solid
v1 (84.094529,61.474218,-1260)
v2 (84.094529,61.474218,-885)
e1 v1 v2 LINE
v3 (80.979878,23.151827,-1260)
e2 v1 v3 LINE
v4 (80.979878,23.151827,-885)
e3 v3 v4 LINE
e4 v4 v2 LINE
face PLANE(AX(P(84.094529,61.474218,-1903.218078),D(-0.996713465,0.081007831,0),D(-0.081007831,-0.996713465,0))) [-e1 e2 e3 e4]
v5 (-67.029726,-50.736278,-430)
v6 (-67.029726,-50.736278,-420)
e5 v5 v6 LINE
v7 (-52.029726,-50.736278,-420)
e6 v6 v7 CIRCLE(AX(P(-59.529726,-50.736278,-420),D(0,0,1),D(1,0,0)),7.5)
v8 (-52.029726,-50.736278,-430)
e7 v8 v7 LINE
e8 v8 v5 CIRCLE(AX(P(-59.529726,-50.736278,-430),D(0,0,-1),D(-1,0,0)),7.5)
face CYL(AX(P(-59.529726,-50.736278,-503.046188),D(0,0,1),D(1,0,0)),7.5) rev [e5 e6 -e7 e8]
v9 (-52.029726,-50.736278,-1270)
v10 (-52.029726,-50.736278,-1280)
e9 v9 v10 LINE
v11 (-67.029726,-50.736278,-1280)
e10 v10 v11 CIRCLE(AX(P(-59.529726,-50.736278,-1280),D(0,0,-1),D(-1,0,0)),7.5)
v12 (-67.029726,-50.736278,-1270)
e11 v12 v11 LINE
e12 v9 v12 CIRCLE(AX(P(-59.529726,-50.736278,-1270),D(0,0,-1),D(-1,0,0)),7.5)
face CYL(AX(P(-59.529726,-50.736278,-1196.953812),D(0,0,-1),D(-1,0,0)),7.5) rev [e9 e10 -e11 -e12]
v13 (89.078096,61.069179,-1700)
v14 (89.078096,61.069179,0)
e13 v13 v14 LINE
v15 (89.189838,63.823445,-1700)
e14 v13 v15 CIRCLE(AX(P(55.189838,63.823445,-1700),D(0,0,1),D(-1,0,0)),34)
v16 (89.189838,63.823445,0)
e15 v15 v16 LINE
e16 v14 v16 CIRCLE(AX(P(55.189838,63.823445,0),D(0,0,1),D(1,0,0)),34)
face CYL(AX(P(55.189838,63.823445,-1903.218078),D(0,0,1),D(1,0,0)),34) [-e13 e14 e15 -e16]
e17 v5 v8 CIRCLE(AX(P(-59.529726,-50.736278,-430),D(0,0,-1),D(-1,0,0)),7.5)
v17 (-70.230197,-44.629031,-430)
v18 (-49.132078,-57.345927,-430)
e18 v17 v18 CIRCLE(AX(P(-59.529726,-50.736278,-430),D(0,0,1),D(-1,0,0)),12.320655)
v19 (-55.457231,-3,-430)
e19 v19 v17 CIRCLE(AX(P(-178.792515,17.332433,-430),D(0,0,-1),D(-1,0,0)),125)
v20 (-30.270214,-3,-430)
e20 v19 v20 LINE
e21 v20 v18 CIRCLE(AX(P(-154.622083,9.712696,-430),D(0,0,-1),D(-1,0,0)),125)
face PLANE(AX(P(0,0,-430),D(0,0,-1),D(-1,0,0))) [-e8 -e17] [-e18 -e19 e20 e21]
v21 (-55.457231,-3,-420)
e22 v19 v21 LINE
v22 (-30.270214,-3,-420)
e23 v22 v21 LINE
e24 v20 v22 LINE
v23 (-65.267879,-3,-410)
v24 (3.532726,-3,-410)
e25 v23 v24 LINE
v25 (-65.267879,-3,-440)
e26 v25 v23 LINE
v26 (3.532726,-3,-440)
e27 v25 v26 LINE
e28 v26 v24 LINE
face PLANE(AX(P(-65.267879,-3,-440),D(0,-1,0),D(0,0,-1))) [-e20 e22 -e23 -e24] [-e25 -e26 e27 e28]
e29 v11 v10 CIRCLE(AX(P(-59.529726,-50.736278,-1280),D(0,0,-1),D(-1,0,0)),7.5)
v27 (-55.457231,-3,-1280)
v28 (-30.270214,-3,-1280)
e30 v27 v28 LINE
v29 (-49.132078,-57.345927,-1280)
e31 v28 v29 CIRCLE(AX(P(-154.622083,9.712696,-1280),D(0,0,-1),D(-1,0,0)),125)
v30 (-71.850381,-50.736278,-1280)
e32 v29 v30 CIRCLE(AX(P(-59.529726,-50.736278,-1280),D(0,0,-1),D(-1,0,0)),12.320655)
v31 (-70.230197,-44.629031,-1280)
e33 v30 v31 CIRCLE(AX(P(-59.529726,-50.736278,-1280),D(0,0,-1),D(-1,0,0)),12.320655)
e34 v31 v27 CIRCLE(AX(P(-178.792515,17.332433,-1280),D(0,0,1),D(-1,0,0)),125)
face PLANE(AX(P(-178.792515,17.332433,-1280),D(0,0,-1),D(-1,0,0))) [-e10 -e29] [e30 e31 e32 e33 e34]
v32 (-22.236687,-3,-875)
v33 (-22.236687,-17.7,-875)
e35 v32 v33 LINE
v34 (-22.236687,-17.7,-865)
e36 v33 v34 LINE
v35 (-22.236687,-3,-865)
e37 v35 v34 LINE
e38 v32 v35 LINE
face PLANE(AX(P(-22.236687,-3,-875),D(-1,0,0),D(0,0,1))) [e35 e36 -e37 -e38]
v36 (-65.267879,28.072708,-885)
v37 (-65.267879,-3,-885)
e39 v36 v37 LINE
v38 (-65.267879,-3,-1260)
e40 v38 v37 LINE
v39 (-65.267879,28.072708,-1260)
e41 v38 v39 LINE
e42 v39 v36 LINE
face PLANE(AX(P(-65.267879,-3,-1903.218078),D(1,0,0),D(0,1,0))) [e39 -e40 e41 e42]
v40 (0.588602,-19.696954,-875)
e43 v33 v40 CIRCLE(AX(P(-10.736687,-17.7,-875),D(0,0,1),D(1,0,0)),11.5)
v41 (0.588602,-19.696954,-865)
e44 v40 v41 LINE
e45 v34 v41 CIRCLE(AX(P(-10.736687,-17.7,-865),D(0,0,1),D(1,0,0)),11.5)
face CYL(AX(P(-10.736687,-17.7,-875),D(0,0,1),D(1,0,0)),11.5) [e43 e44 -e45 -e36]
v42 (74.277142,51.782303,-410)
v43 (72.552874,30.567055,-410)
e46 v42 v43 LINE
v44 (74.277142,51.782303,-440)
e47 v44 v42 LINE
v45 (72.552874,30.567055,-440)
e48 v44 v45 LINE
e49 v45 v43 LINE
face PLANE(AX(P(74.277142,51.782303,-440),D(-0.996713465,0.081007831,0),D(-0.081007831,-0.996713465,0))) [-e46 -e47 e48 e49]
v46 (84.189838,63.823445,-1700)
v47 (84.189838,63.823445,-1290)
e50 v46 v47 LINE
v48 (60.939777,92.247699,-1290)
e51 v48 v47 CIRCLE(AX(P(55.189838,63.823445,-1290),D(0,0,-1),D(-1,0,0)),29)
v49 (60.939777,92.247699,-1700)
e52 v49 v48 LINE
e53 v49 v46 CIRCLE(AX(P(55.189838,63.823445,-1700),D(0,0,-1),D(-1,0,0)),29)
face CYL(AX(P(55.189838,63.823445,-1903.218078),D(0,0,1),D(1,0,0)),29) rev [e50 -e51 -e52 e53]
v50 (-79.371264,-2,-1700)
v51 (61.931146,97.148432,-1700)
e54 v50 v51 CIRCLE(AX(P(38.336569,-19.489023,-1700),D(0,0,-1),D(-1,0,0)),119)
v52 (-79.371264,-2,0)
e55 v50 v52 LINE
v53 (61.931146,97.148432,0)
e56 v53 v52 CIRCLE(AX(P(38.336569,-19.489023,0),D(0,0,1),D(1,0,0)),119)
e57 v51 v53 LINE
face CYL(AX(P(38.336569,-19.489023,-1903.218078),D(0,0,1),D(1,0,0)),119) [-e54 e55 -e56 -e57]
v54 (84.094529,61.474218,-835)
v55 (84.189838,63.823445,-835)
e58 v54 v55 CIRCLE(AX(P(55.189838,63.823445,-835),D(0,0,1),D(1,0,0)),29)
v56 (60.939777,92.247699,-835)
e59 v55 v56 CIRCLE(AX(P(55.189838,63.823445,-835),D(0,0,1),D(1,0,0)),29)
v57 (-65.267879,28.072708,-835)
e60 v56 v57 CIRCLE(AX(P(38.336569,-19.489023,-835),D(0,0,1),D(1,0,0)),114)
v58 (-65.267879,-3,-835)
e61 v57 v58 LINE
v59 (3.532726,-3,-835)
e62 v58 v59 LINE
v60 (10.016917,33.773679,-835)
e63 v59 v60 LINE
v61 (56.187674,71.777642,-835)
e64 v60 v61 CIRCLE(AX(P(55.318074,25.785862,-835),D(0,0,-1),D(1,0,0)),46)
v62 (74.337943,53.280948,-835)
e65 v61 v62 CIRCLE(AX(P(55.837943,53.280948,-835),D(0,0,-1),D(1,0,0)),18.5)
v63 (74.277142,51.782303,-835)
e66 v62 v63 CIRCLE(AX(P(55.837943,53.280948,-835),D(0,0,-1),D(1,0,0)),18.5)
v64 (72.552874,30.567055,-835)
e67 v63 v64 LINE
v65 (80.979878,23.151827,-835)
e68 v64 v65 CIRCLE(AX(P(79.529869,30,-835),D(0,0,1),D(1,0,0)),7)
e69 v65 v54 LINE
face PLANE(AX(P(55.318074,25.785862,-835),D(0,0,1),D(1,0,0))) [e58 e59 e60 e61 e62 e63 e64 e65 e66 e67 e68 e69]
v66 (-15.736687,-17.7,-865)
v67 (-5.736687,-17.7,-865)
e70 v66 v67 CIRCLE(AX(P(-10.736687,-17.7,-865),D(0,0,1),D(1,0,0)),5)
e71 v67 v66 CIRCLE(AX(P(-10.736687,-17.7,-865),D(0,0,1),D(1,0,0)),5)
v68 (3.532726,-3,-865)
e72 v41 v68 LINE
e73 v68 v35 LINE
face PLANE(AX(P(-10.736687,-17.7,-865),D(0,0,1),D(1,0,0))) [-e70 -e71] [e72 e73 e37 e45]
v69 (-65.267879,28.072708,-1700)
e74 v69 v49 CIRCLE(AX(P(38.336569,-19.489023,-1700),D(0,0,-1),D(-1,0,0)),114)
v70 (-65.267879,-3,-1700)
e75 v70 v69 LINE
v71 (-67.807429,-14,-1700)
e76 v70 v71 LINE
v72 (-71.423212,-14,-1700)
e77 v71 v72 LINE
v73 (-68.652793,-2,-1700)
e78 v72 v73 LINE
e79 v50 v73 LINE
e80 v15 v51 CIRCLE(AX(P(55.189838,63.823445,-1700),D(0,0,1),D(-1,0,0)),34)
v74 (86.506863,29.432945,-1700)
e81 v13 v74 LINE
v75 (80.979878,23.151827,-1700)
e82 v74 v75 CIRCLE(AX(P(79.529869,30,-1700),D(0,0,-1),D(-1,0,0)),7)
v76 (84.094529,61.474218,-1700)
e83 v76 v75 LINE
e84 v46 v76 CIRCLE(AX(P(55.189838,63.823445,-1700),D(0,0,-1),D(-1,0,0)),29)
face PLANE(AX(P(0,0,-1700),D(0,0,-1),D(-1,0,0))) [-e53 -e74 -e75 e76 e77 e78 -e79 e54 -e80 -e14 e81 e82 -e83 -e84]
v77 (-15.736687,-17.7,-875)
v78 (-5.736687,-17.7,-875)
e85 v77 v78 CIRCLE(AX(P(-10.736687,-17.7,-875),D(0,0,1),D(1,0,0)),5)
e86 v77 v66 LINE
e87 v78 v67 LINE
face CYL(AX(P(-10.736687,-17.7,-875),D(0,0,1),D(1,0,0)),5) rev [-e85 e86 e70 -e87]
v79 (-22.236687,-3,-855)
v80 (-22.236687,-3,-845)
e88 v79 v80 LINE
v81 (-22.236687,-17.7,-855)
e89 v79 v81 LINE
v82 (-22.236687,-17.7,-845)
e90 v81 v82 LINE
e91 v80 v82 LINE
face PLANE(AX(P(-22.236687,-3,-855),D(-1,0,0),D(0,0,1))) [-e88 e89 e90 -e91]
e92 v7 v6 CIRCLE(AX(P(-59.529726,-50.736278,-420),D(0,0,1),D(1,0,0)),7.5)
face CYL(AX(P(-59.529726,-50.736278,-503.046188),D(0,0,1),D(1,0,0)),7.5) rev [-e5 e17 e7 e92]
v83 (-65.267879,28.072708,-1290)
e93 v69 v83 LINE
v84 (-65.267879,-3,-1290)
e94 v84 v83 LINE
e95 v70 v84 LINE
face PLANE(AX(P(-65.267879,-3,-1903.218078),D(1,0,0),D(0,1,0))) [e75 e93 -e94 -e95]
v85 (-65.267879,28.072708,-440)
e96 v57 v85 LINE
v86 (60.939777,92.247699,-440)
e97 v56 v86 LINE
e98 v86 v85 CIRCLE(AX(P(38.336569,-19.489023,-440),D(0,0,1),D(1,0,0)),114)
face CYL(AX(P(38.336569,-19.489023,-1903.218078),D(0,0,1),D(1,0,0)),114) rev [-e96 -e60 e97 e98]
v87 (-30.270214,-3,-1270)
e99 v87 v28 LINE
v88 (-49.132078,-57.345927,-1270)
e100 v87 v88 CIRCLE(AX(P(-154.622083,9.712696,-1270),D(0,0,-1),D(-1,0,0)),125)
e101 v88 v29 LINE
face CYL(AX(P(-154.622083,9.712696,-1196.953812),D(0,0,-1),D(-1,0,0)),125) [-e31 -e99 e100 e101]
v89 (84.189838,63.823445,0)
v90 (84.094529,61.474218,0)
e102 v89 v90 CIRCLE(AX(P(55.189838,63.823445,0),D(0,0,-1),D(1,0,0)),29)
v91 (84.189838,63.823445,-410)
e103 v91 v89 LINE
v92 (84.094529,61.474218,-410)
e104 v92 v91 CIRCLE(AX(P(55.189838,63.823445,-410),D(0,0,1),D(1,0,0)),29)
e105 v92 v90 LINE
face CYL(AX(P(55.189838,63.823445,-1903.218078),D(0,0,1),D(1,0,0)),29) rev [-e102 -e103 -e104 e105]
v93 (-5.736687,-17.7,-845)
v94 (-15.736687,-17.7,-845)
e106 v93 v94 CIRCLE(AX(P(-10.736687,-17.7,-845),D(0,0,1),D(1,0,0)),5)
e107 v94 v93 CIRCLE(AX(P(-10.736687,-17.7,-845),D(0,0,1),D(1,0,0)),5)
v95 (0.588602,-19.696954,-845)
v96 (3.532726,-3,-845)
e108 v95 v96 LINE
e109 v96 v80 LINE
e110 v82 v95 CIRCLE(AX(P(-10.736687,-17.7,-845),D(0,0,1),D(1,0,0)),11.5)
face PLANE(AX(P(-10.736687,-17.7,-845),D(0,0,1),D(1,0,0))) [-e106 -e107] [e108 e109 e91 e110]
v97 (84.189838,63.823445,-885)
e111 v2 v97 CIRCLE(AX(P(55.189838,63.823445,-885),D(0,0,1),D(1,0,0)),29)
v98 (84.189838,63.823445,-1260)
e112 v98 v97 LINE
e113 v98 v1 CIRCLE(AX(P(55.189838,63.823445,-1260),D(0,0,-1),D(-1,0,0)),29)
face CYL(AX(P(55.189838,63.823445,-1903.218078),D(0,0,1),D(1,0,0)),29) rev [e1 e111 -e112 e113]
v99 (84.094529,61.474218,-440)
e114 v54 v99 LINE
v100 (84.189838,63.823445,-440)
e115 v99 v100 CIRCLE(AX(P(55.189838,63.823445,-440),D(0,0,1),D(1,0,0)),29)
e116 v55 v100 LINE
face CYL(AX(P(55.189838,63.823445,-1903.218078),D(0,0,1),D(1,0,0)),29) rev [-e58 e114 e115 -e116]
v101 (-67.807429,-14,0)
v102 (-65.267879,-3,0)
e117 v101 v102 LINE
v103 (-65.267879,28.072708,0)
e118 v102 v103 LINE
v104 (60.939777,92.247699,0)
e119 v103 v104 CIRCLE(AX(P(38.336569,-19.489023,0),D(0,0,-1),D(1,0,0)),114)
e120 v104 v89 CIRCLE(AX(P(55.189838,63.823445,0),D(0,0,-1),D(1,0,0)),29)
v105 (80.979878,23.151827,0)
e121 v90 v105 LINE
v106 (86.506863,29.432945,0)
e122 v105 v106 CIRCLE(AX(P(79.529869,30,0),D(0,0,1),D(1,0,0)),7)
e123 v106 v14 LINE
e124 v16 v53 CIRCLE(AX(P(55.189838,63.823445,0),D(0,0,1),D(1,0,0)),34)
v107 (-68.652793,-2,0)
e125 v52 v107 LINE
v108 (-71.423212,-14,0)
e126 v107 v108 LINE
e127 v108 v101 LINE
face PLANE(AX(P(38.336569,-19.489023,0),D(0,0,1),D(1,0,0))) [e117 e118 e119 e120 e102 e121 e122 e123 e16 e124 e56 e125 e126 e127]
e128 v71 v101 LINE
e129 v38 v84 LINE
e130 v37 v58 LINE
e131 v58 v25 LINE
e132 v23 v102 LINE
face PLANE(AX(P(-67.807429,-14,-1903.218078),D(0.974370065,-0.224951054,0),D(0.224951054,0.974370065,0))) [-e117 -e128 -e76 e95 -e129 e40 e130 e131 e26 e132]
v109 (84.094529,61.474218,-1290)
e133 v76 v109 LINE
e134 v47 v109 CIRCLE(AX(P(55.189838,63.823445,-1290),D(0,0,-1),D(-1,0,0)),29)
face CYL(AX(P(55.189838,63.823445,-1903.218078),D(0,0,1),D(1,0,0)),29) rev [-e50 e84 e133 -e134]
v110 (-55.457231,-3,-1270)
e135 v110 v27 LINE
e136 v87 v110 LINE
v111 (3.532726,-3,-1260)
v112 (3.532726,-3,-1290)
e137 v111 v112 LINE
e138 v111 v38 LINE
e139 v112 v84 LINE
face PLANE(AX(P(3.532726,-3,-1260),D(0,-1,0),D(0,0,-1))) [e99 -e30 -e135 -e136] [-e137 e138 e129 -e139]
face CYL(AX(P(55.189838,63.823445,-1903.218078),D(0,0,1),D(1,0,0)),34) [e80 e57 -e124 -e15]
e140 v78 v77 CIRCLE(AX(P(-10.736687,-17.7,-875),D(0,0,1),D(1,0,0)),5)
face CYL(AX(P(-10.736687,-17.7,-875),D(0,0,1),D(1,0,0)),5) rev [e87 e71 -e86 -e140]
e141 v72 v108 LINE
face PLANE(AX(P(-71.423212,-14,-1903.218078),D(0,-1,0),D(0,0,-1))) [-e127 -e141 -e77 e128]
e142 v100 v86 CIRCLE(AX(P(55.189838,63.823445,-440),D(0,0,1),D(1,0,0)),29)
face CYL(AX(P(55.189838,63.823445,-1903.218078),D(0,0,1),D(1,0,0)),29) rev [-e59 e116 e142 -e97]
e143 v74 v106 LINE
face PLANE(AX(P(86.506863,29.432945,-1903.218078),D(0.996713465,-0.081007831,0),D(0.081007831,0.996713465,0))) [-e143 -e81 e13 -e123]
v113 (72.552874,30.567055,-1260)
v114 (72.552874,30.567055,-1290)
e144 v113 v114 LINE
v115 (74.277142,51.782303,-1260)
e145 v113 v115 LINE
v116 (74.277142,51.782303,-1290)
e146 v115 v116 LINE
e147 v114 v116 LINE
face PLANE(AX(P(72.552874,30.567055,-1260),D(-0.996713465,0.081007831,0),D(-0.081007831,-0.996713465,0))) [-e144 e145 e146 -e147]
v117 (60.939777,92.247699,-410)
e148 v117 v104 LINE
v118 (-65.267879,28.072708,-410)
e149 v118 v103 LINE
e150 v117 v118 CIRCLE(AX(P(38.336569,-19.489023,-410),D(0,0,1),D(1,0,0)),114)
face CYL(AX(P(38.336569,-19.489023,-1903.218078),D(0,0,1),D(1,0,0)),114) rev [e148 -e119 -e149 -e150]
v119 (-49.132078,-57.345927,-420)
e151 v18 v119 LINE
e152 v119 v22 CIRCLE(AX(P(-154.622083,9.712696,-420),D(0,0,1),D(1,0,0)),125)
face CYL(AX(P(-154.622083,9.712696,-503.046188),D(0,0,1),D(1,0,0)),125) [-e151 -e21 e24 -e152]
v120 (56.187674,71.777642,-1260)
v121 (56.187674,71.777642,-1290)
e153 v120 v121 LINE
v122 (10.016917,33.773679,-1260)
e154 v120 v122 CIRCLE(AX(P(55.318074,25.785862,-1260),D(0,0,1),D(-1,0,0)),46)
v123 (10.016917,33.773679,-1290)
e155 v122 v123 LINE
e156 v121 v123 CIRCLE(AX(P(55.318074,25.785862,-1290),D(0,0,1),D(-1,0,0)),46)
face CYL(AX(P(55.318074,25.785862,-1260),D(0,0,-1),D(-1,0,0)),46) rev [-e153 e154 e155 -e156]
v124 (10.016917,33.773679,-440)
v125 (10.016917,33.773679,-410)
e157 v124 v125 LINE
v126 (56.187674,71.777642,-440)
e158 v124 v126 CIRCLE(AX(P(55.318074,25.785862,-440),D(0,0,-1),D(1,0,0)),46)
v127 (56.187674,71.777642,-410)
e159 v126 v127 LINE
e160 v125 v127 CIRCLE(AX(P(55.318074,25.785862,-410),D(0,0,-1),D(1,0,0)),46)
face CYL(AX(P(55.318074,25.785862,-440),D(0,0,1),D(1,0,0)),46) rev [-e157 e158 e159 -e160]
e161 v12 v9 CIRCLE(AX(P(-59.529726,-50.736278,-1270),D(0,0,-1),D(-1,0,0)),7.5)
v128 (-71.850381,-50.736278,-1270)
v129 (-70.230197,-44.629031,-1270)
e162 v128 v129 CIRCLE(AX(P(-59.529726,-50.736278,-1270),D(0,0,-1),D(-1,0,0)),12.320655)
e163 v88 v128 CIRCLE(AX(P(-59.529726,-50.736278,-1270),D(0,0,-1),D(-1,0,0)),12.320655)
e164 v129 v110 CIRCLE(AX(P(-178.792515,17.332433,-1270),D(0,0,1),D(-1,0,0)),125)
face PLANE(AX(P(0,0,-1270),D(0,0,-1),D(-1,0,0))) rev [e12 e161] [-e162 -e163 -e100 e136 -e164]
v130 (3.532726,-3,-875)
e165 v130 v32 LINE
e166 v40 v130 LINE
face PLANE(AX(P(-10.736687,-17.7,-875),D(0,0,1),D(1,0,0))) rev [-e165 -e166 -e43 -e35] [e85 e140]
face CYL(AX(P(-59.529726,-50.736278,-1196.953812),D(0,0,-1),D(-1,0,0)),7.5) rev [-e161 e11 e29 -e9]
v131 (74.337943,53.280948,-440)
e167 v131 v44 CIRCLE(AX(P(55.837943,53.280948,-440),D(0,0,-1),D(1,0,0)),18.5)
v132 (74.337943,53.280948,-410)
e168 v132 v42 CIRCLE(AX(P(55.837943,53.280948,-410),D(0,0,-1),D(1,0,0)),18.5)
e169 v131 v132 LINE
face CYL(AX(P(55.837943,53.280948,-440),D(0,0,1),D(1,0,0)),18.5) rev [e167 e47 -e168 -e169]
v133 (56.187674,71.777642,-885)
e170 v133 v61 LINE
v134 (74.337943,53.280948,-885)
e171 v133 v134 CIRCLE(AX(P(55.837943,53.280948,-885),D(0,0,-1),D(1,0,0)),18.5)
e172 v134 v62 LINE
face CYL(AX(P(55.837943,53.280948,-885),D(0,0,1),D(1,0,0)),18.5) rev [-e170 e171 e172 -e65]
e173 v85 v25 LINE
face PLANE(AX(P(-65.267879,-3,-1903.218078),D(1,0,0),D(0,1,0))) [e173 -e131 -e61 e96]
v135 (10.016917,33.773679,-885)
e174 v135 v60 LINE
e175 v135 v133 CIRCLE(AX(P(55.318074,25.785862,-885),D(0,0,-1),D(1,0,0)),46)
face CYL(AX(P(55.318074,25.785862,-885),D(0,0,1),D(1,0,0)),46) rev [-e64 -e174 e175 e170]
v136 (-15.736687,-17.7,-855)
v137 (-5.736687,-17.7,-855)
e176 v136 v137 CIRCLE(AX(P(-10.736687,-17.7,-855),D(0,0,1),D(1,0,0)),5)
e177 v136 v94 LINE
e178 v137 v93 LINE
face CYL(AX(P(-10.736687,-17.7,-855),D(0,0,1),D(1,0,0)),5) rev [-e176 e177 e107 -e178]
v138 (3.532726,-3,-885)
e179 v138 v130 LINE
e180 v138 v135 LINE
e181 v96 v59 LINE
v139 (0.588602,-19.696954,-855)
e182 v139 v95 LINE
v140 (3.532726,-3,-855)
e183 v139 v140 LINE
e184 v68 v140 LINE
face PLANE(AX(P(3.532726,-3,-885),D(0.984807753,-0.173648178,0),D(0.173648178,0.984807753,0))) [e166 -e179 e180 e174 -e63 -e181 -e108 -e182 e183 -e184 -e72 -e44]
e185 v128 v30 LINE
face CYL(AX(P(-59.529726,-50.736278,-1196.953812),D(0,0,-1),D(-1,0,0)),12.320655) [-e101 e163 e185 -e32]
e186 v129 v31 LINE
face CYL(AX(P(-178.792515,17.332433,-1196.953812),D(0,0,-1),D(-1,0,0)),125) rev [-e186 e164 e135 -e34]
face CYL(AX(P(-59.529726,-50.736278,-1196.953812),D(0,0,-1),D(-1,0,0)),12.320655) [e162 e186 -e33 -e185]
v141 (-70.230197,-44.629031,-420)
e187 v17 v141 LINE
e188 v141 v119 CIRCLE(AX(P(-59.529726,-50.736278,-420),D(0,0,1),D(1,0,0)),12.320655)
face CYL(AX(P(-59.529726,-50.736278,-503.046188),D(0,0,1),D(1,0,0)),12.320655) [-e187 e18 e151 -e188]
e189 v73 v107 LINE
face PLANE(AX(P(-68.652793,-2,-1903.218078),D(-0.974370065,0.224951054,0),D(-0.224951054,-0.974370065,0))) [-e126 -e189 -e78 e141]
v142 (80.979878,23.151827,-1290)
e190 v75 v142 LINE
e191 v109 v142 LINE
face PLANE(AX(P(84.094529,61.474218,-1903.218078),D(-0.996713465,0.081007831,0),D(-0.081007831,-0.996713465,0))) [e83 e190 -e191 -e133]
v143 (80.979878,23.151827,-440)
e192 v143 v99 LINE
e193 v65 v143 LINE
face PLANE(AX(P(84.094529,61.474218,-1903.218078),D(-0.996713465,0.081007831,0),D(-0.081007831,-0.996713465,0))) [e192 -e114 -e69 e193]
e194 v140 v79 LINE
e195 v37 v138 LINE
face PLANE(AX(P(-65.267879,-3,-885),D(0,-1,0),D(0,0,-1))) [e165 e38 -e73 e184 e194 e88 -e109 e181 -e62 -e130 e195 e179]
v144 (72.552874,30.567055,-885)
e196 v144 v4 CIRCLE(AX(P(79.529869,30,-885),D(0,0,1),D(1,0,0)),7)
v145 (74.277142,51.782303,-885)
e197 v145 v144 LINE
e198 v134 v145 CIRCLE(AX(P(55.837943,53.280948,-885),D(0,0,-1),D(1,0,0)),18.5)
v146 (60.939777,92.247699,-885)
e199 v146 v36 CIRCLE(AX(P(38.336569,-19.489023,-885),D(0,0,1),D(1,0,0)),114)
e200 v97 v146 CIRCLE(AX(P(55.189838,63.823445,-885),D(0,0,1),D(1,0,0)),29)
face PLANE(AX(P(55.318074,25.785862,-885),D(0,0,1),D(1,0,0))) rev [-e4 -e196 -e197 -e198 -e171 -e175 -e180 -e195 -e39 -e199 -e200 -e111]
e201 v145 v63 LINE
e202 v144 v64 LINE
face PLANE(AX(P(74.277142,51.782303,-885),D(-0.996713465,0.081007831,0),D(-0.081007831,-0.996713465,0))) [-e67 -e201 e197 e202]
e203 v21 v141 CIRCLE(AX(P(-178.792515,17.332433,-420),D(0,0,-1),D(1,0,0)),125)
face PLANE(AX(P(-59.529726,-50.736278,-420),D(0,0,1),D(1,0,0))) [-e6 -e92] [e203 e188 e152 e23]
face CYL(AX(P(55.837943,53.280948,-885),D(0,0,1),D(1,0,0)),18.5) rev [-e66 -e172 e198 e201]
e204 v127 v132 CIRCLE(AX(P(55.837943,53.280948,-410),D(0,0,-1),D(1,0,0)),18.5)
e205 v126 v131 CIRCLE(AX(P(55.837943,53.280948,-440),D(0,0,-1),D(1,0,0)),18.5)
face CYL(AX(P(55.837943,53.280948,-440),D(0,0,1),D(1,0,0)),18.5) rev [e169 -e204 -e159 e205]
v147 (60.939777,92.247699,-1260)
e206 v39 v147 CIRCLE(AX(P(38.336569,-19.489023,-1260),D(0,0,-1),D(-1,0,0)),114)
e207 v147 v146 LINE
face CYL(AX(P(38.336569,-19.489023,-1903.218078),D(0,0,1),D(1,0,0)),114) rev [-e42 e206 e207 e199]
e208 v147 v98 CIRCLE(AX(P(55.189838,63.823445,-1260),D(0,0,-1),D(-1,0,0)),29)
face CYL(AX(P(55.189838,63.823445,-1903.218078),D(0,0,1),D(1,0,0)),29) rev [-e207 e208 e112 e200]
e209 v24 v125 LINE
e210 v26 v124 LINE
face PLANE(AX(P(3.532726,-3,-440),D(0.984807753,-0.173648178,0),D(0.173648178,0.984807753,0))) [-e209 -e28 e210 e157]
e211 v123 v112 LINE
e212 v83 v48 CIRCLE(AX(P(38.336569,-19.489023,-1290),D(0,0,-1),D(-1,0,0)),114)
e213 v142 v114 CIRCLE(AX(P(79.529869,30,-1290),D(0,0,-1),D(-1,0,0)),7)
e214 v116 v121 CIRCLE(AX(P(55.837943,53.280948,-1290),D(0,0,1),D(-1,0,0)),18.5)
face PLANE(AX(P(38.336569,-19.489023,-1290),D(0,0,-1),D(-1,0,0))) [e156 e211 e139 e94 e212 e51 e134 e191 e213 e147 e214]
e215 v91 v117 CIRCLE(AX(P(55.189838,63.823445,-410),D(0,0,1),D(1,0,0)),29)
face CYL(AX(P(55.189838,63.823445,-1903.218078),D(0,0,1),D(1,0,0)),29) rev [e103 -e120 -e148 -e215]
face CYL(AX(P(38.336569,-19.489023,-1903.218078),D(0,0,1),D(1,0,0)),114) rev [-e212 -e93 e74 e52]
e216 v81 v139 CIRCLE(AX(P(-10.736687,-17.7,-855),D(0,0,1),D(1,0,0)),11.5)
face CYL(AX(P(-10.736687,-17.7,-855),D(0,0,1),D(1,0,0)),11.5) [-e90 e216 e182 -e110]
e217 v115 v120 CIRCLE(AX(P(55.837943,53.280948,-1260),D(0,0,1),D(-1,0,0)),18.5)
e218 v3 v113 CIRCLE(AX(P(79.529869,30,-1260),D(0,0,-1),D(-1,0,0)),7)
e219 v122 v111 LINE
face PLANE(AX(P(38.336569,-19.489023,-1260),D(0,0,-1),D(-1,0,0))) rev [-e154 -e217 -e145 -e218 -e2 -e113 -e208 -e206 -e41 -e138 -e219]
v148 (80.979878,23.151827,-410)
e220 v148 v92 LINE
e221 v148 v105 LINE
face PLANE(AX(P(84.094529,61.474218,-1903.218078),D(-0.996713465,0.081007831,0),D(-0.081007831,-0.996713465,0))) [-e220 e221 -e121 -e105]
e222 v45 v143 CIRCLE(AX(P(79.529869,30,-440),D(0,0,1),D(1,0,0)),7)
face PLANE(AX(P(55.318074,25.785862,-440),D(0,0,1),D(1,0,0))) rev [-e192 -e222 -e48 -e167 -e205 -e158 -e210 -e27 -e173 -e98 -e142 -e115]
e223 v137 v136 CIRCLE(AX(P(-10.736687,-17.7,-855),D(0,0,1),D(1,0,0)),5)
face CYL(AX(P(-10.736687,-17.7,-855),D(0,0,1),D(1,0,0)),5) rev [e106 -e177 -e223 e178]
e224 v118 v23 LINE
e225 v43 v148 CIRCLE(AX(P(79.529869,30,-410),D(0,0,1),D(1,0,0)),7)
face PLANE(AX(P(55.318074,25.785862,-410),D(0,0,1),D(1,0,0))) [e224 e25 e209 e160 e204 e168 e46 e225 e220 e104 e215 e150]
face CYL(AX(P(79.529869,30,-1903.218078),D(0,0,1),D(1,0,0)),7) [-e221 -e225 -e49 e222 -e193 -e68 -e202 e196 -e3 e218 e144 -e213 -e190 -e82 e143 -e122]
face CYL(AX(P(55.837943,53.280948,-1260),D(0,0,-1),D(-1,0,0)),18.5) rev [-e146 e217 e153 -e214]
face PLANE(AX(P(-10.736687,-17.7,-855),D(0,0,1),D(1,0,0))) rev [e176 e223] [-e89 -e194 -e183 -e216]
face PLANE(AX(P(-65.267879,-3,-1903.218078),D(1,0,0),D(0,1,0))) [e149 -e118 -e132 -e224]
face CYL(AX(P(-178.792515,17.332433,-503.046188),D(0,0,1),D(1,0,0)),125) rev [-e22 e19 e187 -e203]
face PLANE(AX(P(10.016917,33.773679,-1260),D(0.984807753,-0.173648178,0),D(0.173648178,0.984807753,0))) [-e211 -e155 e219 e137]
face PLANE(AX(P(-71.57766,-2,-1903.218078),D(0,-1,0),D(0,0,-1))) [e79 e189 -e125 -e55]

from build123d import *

# Parameters (mm, degrees)
BOSS_EXTRUDE1_DEPTH = 1700
BOSS_EXTRUDE2_START = -30
BOSS_EXTRUDE2_DEPTH = 30
BOSS_EXTRUDE3_DEPTH = 10
BOSS_EXTRUDE4_DEPTH = 30
BOSS_EXTRUDE5_START = -10
SKETCH5_R           = 7.5
BOSS_EXTRUDE5_DEPTH = 10
BOSS_EXTRUDE6_DEPTH = 50
BOSS_EXTRUDE7_DEPTH = 10
BOSS_EXTRUDE8_DEPTH = 10


with BuildPart() as part:
    # Sketch1 → Boss-Extrude1 (new body)
    with BuildSketch(Plane.XY):
        with BuildLine():
            Line((-65.267879059, -3), (-65.267879058, 28.072707798))
            ThreePointArc((-65.267879058, 28.072707798), (-13.334579465, 82.12835912), (60.939776886, 92.247698777))
            ThreePointArc((60.939776886, 92.247698777), (78.362831346, 81.25939595), (84.094528642, 61.474217866))
            Line((84.094528642, 61.474217866), (80.979878482, 23.151827152))
            ThreePointArc((80.979878482, 23.151827152), (84.785028981, 25.375793105), (86.506862858, 29.432945182))
            Line((86.506862858, 29.432945182), (89.078095967, 61.069178711))
            ThreePointArc((89.078095967, 61.069178711), (82.358174999, 84.265594396), (61.931145633, 97.148432192))
            ThreePointArc((61.931145633, 97.148432192), (-30.014942614, 77.922838587), (-79.371264048, -2))
            Line((-79.371264048, -2), (-72.901993076, -2))
            Line((-72.901993076, -2), (-71.577659573, -2))
            Line((-71.577659573, -2), (-68.652793332, -2))
            Line((-68.652793332, -2), (-71.423211626, -14))
            Line((-71.423211626, -14), (-67.807429161, -14))
            Line((-67.807429161, -14), (-65.267879059, -3))
        make_face()
    extrude(amount=-BOSS_EXTRUDE1_DEPTH)

    # Sketch2 → Boss-Extrude2 (add)
    with BuildSketch(Plane(origin=(0, 0, -1290), x_dir=(-1, 0, 0), z_dir=(0, 0, -1)).offset(BOSS_EXTRUDE2_START)):
        with BuildLine():
            Line((-3.532725505, -3), (65.267879058, -3))
            Line((65.267879058, -3), (65.267879058, 28.072707798))
            ThreePointArc((65.267879058, 28.072707798), (13.334579465, 82.12835912), (-60.939776886, 92.247698777))
            ThreePointArc((-60.939776886, 92.247698777), (-78.362831346, 81.25939595), (-84.094528642, 61.474217866))
            Line((-84.094528642, 61.474217866), (-80.979878482, 23.151827152))
            ThreePointArc((-80.979878482, 23.151827152), (-74.905661708, 24.744839622), (-72.552874348, 30.567054818))
            Line((-72.552874348, 30.567054818), (-74.277142478, 51.782303262))
            ThreePointArc((-74.277142478, 51.782303262), (-69.556885099, 65.692259025), (-56.187673771, 71.777642129))
            ThreePointArc((-56.187673771, 71.777642129), (-26.084255804, 61.301829041), (-10.01691723, 33.773678645))
            Line((-10.01691723, 33.773678645), (-3.532725505, -3))
        make_face()
    extrude(amount=BOSS_EXTRUDE2_DEPTH)

    # Sketch3 → Boss-Extrude3 (add)
    with BuildSketch(Plane(origin=(0, 0, -1280), x_dir=(-1, 0, 0), z_dir=(0, 0, -1))):
        with BuildLine():
            Line((55.457231442, -3), (30.270213705, -3))
            ThreePointArc((30.270213705, -3), (36.532321703, -31.272768855), (49.132078223, -57.345927293))
            ThreePointArc((49.132078223, -57.345927293), (65.889976377, -61.288327787), (70.23019688, -44.629031338))
            ThreePointArc((70.23019688, -44.629031338), (60.990271903, -24.472249888), (55.457231442, -3))
        make_face()
        with BuildLine():
            ThreePointArc((52.029725897, -50.736277995), (59.529725897, -58.236277995), (67.029725897, -50.736277995))
            ThreePointArc((67.029725897, -50.736277995), (59.529725897, -43.236277995), (52.029725897, -50.736277995))
        make_face(mode=Mode.SUBTRACT)
    extrude(amount=-BOSS_EXTRUDE3_DEPTH)

    # Sketch4 → Boss-Extrude4 (add)
    with BuildSketch(Plane.XY.offset(-410)):
        with BuildLine():
            Line((3.532725505, -3), (10.01691723, 33.773678645))
            ThreePointArc((10.01691723, 33.773678645), (26.084255804, 61.301829041), (56.187673771, 71.777642129))
            ThreePointArc((56.187673771, 71.777642129), (69.556885099, 65.692259025), (74.277142478, 51.782303262))
            Line((74.277142478, 51.782303262), (72.552874348, 30.567054818))
            ThreePointArc((72.552874348, 30.567054818), (74.905661708, 24.744839622), (80.979878482, 23.151827152))
            Line((80.979878482, 23.151827152), (84.094528642, 61.474217866))
            ThreePointArc((84.094528642, 61.474217866), (78.362831346, 81.25939595), (60.939776886, 92.247698777))
            ThreePointArc((60.939776886, 92.247698777), (-13.334579465, 82.12835912), (-65.267879058, 28.072707798))
            Line((-65.267879058, 28.072707798), (-65.267879058, -3))
            Line((-65.267879058, -3), (3.532725505, -3))
        make_face()
    extrude(amount=-BOSS_EXTRUDE4_DEPTH)

    # Sketch5 → Boss-Extrude5 (add)
    with BuildSketch(Plane.XY.offset(-420).offset(BOSS_EXTRUDE5_START)):
        with BuildLine():
            Line((-30.270213705, -3), (-55.457231442, -3))
            ThreePointArc((-55.457231442, -3), (-60.990271903, -24.472249888), (-70.23019688, -44.629031338))
            ThreePointArc((-70.23019688, -44.629031338), (-65.889976377, -61.288327787), (-49.132078223, -57.345927293))
            ThreePointArc((-49.132078223, -57.345927293), (-36.532321703, -31.272768855), (-30.270213705, -3))
        make_face()
        with Locations(Location((-59.529725897, -50.736277995, 0), (0, 0, 180))):
            Circle(SKETCH5_R, mode=Mode.SUBTRACT)
    extrude(amount=BOSS_EXTRUDE5_DEPTH)

    # Sketch7 → Boss-Extrude6 (add)
    with BuildSketch(Plane.XY.offset(-835)):
        with BuildLine():
            Line((3.532725505, -3), (10.01691723, 33.773678645))
            ThreePointArc((10.01691723, 33.773678645), (26.084255804, 61.301829041), (56.187673771, 71.777642129))
            ThreePointArc((56.187673771, 71.777642129), (69.556885099, 65.692259025), (74.277142478, 51.782303262))
            Line((74.277142478, 51.782303262), (72.552874348, 30.567054818))
            ThreePointArc((72.552874348, 30.567054818), (74.905661708, 24.744839622), (80.979878482, 23.151827152))
            Line((80.979878482, 23.151827152), (84.094528642, 61.474217866))
            ThreePointArc((84.094528642, 61.474217866), (78.362831346, 81.25939595), (60.939776886, 92.247698777))
            ThreePointArc((60.939776886, 92.247698777), (-13.334579465, 82.12835912), (-65.267879058, 28.072707798))
            Line((-65.267879058, 28.072707798), (-65.267879059, -3))
            Line((-65.267879059, -3), (3.532725505, -3))
        make_face()
    extrude(amount=-BOSS_EXTRUDE6_DEPTH)

    # Sketch8 → Boss-Extrude7 (add)
    with BuildSketch(Plane.XY.offset(-845)):
        with BuildLine():
            Line((-22.236687148, -3), (-22.236687148, -17.7))
            ThreePointArc((-22.236687148, -17.7), (-11.738978189, -29.156239028), (0.588602012, -19.696954043))
            Line((0.588602012, -19.696954043), (3.532725505, -3))
            Line((3.532725505, -3), (-22.236687148, -3))
        make_face()
        with BuildLine():
            ThreePointArc((-5.736687148, -17.7), (-10.736687148, -12.7), (-15.736687148, -17.7))
            ThreePointArc((-15.736687148, -17.7), (-10.736687148, -22.7), (-5.736687148, -17.7))
        make_face(mode=Mode.SUBTRACT)
    extrude(amount=-BOSS_EXTRUDE7_DEPTH)

    # Sketch9 → Boss-Extrude8 (add)
    with BuildSketch(Plane.XY.offset(-865)):
        with BuildLine():
            Line((-22.236687148, -3), (-22.236687148, -17.699999999))
            ThreePointArc((-22.236687148, -17.699999999), (-11.73897819, -29.156239028), (0.588602012, -19.696954043))
            Line((0.588602012, -19.696954043), (3.532725505, -3))
            Line((3.532725505, -3), (-22.236687148, -3))
        make_face()
        with BuildLine():
            ThreePointArc((-5.736687148, -17.7), (-10.736687148, -12.7), (-15.736687148, -17.7))
            ThreePointArc((-15.736687148, -17.7), (-10.736687148, -22.7), (-5.736687148, -17.7))
        make_face(mode=Mode.SUBTRACT)
    extrude(amount=-BOSS_EXTRUDE8_DEPTH)


solid = part.part
